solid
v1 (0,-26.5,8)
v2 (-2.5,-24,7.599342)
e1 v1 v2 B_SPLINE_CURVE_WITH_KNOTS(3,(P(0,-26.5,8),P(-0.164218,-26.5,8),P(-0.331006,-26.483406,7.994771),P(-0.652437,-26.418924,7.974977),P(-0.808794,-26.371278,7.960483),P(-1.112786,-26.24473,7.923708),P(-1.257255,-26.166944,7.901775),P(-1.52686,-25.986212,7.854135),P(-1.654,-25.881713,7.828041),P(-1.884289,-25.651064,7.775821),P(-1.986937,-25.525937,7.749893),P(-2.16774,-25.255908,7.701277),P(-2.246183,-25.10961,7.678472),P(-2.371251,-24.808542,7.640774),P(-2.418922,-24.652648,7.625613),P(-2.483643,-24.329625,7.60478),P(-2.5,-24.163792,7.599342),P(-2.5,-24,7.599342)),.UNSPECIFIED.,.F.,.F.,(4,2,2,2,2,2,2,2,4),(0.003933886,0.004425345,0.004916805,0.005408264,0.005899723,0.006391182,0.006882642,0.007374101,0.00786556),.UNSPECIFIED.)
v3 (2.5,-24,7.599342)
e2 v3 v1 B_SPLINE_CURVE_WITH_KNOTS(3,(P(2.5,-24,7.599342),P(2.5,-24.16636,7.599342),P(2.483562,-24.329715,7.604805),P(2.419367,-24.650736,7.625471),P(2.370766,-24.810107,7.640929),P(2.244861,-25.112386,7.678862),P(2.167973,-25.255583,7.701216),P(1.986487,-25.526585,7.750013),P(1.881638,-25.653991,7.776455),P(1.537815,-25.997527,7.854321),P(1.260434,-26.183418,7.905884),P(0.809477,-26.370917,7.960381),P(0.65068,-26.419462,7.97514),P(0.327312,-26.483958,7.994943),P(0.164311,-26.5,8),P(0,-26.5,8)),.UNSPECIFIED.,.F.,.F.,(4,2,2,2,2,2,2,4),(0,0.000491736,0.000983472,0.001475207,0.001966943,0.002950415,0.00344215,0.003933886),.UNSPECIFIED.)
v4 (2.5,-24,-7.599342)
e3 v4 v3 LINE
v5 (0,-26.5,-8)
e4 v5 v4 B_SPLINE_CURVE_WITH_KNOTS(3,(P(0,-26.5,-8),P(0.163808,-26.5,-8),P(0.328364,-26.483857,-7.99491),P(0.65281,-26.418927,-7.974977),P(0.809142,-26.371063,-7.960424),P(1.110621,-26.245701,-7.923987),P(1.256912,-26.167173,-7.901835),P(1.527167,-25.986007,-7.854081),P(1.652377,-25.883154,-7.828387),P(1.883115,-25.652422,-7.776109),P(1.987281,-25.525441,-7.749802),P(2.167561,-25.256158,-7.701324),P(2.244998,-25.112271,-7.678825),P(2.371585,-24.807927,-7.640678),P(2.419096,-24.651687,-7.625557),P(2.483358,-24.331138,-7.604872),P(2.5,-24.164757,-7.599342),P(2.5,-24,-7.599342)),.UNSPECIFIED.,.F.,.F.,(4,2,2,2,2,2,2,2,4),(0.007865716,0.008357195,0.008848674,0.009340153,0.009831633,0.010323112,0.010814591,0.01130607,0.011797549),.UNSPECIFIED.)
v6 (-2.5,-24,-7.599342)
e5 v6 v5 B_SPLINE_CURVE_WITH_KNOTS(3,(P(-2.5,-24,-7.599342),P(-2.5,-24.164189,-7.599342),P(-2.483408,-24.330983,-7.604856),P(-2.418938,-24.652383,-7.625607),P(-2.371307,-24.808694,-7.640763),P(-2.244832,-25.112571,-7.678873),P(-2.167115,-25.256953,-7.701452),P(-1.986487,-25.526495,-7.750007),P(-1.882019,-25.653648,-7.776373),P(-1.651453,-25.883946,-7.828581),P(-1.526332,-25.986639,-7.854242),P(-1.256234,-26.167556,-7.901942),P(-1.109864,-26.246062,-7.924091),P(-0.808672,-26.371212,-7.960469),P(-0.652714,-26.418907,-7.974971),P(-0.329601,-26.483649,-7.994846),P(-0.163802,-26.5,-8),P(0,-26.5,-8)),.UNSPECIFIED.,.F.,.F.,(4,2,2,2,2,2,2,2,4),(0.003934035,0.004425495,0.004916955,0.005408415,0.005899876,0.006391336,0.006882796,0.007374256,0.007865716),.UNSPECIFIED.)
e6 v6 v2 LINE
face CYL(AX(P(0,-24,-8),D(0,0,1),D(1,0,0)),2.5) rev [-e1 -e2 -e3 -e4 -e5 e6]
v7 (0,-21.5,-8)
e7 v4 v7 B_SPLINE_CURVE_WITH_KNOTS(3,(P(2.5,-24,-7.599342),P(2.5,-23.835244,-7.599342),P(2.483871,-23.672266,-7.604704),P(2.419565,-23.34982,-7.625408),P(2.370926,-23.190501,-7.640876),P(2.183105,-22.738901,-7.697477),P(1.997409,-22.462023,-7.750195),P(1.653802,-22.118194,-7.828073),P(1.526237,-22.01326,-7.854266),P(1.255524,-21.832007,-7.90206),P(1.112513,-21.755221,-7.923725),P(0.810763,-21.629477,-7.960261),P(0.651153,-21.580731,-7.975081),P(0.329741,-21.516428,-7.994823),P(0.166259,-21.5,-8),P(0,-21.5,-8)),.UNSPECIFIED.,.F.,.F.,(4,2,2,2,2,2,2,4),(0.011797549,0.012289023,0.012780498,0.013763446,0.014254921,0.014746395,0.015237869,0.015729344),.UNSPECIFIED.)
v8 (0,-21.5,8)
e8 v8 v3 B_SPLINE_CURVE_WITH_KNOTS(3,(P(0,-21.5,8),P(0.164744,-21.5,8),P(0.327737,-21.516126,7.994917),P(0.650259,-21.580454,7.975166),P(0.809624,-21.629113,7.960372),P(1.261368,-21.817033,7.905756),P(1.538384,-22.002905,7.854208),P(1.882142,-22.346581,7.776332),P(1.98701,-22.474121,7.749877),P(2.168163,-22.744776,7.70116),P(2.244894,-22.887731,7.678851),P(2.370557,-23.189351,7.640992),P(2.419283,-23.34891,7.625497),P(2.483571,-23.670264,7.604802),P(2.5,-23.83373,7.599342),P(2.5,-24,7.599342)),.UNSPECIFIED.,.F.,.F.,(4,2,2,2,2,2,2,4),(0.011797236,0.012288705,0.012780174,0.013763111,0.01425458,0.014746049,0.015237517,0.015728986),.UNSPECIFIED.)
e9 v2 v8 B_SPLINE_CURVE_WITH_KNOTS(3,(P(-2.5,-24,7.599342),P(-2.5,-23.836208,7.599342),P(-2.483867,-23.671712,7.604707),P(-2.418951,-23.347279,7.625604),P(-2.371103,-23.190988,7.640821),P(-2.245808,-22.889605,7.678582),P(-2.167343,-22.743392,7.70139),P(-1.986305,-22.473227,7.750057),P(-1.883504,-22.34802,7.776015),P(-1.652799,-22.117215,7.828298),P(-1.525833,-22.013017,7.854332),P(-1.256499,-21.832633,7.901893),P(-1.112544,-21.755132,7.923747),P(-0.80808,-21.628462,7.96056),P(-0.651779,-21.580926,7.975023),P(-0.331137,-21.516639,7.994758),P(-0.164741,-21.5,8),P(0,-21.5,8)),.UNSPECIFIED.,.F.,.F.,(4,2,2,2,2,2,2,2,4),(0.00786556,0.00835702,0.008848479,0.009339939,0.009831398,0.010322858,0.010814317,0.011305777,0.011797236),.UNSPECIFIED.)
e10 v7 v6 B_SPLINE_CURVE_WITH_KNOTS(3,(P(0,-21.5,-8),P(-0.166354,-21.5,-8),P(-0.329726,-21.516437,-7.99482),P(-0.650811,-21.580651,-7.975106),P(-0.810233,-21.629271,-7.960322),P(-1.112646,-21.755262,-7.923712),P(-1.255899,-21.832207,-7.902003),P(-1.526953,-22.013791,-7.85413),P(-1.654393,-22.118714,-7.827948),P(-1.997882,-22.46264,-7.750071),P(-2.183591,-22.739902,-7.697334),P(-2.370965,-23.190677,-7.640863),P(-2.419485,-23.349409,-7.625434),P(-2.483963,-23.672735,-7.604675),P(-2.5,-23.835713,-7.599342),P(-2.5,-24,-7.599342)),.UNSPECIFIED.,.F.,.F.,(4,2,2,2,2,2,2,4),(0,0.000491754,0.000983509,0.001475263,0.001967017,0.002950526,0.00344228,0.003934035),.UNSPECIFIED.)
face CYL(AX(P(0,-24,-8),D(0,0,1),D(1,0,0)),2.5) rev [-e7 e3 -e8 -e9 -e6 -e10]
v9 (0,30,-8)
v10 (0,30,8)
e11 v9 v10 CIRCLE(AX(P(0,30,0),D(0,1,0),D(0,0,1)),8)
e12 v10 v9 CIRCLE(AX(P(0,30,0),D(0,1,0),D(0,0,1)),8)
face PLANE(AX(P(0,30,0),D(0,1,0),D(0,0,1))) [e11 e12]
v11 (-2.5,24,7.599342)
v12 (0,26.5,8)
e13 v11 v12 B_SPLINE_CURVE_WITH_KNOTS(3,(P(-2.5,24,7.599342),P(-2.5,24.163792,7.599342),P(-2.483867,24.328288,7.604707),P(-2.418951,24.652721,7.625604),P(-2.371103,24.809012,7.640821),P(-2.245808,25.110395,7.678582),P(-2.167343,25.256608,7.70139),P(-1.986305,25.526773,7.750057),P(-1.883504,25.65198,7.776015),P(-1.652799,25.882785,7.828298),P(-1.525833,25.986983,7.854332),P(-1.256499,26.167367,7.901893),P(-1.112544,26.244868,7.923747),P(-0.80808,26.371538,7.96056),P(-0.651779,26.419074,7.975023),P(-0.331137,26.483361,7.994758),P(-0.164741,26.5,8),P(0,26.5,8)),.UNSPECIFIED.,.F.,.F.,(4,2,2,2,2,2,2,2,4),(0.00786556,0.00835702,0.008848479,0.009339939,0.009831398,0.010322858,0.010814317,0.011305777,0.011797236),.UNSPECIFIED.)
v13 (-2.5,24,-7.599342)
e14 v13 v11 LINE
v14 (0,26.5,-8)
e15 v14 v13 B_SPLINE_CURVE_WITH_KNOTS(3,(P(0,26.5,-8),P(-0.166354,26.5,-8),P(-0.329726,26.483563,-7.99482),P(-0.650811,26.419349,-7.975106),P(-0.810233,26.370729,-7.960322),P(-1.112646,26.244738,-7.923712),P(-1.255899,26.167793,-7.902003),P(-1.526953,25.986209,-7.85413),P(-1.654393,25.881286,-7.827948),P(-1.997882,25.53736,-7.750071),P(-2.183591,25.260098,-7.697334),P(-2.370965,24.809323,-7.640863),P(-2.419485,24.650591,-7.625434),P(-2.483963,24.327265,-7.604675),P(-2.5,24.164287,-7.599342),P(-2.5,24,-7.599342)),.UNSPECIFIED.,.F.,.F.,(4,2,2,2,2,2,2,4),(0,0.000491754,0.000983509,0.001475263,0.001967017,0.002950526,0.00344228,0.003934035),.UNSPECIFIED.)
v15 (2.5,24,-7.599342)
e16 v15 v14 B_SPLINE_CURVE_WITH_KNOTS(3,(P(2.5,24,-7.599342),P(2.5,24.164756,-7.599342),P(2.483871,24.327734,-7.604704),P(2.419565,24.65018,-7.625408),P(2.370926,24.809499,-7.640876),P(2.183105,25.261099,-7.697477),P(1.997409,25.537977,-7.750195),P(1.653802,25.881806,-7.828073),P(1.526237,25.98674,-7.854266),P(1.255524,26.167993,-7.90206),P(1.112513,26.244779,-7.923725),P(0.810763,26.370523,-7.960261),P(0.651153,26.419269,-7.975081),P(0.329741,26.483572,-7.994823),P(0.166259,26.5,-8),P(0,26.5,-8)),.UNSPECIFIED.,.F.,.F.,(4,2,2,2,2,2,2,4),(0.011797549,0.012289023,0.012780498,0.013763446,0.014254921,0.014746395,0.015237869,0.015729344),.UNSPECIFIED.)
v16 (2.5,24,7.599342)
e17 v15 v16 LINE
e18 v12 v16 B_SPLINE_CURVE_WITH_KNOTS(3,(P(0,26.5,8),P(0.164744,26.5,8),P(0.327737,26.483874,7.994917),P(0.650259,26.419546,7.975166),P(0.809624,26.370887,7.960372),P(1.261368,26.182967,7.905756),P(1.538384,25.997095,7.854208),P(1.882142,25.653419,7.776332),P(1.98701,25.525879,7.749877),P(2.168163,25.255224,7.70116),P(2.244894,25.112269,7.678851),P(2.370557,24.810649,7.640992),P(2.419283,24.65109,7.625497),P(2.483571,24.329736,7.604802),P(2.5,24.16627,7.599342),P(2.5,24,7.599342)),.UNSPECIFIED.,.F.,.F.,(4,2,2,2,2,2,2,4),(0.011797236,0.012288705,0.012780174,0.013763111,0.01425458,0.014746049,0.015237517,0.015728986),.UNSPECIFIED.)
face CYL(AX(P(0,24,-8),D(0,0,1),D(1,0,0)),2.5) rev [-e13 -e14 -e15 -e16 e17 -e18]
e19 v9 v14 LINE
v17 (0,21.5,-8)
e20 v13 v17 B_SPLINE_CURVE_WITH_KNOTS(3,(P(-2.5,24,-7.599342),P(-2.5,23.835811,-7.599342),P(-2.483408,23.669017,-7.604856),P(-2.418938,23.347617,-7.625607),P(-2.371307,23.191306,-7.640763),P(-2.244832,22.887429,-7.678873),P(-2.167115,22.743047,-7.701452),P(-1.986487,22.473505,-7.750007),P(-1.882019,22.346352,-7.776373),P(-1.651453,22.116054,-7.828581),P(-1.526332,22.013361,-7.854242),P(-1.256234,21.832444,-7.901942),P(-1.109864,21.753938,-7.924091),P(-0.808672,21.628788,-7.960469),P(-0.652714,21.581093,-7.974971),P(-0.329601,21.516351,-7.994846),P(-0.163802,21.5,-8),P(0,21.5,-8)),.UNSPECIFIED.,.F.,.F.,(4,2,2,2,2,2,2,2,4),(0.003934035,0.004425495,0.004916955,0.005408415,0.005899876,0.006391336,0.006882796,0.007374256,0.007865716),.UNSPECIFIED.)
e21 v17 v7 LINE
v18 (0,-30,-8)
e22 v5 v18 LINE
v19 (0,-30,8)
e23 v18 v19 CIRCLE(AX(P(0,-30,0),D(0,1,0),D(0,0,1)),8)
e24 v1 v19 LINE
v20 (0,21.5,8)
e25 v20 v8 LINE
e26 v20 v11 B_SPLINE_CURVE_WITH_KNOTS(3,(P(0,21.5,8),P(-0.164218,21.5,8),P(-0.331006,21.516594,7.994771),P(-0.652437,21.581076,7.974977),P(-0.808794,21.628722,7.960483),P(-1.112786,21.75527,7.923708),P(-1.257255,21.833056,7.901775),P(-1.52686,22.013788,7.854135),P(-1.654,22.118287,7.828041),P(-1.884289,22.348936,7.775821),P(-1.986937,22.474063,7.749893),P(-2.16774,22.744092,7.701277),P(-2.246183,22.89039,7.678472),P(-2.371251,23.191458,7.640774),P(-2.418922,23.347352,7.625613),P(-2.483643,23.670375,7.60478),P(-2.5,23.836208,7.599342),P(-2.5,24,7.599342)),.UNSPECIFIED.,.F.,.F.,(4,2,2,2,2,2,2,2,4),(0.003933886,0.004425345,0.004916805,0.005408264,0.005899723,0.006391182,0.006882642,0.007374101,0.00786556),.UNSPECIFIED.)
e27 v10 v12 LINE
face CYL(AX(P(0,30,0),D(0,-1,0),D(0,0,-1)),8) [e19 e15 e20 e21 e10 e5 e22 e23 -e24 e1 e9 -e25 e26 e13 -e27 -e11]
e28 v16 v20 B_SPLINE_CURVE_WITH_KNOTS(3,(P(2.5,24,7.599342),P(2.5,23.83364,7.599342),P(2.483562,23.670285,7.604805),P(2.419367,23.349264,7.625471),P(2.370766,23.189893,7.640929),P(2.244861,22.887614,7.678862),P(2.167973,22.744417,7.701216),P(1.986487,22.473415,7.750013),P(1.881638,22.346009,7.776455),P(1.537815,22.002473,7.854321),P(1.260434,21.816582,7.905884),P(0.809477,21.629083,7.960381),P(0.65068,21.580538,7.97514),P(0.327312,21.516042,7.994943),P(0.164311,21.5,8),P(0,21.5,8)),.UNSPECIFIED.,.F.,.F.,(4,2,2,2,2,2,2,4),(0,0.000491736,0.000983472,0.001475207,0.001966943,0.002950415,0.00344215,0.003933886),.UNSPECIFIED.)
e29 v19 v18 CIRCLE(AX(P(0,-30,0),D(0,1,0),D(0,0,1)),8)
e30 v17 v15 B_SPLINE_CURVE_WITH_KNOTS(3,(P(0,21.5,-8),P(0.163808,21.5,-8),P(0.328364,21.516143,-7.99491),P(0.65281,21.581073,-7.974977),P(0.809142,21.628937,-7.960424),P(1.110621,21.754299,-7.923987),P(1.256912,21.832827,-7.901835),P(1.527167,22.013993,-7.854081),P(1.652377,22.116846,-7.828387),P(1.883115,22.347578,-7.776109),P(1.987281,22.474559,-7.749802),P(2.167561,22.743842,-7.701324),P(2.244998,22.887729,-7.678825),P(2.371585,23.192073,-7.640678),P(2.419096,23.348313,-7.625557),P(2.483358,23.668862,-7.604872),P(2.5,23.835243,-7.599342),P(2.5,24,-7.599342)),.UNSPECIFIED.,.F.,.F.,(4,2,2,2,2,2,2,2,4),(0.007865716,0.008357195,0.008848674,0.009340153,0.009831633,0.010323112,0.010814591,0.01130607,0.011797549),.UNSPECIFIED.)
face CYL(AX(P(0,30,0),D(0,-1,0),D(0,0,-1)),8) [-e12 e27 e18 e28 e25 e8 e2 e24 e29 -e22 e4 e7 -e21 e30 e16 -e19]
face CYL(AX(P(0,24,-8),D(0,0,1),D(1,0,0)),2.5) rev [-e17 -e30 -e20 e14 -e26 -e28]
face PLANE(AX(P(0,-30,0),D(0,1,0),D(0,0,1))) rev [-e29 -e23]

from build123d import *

# Parameters (mm, degrees)
PIN_PROFILE_16_R       = 8
PIN_BODY_16X60_DEPTH   = 30
CROSS_HOLES_DEPTH      = 33.062439084
CROSS_HOLES_DEPTH_BACK = 33.062439084
CROSS_HOLE_PROFILE_R   = 2.5


with BuildPart() as part:
    # Pin Profile Ø16 → Pin Body Ø16x60 (new, symmetric)
    with BuildSketch(Plane(origin=(0, 0, 0), x_dir=(1, 0, 0), z_dir=(0, 1, 0))):
        with Locations(Location((0, 0, 0), (0, 0, 270))):
            Circle(PIN_PROFILE_16_R)
    extrude(amount=PIN_BODY_16X60_DEPTH, both=True)

    # Cross Hole Profile → Cross Holes (cut, two sides: drawn at the far end of the back side and taken through both)
    with BuildSketch(Plane.XY.offset(-CROSS_HOLES_DEPTH_BACK)):
        with Locations(Location((0, 24, 0), (0, 0, 89.99999999))):
            Circle(CROSS_HOLE_PROFILE_R)
        with Locations(Location((0, -24, 0), (0, 0, 89.99999999))):
            Circle(CROSS_HOLE_PROFILE_R)
    extrude(amount=CROSS_HOLES_DEPTH + CROSS_HOLES_DEPTH_BACK, mode=Mode.SUBTRACT)


solid = part.part
